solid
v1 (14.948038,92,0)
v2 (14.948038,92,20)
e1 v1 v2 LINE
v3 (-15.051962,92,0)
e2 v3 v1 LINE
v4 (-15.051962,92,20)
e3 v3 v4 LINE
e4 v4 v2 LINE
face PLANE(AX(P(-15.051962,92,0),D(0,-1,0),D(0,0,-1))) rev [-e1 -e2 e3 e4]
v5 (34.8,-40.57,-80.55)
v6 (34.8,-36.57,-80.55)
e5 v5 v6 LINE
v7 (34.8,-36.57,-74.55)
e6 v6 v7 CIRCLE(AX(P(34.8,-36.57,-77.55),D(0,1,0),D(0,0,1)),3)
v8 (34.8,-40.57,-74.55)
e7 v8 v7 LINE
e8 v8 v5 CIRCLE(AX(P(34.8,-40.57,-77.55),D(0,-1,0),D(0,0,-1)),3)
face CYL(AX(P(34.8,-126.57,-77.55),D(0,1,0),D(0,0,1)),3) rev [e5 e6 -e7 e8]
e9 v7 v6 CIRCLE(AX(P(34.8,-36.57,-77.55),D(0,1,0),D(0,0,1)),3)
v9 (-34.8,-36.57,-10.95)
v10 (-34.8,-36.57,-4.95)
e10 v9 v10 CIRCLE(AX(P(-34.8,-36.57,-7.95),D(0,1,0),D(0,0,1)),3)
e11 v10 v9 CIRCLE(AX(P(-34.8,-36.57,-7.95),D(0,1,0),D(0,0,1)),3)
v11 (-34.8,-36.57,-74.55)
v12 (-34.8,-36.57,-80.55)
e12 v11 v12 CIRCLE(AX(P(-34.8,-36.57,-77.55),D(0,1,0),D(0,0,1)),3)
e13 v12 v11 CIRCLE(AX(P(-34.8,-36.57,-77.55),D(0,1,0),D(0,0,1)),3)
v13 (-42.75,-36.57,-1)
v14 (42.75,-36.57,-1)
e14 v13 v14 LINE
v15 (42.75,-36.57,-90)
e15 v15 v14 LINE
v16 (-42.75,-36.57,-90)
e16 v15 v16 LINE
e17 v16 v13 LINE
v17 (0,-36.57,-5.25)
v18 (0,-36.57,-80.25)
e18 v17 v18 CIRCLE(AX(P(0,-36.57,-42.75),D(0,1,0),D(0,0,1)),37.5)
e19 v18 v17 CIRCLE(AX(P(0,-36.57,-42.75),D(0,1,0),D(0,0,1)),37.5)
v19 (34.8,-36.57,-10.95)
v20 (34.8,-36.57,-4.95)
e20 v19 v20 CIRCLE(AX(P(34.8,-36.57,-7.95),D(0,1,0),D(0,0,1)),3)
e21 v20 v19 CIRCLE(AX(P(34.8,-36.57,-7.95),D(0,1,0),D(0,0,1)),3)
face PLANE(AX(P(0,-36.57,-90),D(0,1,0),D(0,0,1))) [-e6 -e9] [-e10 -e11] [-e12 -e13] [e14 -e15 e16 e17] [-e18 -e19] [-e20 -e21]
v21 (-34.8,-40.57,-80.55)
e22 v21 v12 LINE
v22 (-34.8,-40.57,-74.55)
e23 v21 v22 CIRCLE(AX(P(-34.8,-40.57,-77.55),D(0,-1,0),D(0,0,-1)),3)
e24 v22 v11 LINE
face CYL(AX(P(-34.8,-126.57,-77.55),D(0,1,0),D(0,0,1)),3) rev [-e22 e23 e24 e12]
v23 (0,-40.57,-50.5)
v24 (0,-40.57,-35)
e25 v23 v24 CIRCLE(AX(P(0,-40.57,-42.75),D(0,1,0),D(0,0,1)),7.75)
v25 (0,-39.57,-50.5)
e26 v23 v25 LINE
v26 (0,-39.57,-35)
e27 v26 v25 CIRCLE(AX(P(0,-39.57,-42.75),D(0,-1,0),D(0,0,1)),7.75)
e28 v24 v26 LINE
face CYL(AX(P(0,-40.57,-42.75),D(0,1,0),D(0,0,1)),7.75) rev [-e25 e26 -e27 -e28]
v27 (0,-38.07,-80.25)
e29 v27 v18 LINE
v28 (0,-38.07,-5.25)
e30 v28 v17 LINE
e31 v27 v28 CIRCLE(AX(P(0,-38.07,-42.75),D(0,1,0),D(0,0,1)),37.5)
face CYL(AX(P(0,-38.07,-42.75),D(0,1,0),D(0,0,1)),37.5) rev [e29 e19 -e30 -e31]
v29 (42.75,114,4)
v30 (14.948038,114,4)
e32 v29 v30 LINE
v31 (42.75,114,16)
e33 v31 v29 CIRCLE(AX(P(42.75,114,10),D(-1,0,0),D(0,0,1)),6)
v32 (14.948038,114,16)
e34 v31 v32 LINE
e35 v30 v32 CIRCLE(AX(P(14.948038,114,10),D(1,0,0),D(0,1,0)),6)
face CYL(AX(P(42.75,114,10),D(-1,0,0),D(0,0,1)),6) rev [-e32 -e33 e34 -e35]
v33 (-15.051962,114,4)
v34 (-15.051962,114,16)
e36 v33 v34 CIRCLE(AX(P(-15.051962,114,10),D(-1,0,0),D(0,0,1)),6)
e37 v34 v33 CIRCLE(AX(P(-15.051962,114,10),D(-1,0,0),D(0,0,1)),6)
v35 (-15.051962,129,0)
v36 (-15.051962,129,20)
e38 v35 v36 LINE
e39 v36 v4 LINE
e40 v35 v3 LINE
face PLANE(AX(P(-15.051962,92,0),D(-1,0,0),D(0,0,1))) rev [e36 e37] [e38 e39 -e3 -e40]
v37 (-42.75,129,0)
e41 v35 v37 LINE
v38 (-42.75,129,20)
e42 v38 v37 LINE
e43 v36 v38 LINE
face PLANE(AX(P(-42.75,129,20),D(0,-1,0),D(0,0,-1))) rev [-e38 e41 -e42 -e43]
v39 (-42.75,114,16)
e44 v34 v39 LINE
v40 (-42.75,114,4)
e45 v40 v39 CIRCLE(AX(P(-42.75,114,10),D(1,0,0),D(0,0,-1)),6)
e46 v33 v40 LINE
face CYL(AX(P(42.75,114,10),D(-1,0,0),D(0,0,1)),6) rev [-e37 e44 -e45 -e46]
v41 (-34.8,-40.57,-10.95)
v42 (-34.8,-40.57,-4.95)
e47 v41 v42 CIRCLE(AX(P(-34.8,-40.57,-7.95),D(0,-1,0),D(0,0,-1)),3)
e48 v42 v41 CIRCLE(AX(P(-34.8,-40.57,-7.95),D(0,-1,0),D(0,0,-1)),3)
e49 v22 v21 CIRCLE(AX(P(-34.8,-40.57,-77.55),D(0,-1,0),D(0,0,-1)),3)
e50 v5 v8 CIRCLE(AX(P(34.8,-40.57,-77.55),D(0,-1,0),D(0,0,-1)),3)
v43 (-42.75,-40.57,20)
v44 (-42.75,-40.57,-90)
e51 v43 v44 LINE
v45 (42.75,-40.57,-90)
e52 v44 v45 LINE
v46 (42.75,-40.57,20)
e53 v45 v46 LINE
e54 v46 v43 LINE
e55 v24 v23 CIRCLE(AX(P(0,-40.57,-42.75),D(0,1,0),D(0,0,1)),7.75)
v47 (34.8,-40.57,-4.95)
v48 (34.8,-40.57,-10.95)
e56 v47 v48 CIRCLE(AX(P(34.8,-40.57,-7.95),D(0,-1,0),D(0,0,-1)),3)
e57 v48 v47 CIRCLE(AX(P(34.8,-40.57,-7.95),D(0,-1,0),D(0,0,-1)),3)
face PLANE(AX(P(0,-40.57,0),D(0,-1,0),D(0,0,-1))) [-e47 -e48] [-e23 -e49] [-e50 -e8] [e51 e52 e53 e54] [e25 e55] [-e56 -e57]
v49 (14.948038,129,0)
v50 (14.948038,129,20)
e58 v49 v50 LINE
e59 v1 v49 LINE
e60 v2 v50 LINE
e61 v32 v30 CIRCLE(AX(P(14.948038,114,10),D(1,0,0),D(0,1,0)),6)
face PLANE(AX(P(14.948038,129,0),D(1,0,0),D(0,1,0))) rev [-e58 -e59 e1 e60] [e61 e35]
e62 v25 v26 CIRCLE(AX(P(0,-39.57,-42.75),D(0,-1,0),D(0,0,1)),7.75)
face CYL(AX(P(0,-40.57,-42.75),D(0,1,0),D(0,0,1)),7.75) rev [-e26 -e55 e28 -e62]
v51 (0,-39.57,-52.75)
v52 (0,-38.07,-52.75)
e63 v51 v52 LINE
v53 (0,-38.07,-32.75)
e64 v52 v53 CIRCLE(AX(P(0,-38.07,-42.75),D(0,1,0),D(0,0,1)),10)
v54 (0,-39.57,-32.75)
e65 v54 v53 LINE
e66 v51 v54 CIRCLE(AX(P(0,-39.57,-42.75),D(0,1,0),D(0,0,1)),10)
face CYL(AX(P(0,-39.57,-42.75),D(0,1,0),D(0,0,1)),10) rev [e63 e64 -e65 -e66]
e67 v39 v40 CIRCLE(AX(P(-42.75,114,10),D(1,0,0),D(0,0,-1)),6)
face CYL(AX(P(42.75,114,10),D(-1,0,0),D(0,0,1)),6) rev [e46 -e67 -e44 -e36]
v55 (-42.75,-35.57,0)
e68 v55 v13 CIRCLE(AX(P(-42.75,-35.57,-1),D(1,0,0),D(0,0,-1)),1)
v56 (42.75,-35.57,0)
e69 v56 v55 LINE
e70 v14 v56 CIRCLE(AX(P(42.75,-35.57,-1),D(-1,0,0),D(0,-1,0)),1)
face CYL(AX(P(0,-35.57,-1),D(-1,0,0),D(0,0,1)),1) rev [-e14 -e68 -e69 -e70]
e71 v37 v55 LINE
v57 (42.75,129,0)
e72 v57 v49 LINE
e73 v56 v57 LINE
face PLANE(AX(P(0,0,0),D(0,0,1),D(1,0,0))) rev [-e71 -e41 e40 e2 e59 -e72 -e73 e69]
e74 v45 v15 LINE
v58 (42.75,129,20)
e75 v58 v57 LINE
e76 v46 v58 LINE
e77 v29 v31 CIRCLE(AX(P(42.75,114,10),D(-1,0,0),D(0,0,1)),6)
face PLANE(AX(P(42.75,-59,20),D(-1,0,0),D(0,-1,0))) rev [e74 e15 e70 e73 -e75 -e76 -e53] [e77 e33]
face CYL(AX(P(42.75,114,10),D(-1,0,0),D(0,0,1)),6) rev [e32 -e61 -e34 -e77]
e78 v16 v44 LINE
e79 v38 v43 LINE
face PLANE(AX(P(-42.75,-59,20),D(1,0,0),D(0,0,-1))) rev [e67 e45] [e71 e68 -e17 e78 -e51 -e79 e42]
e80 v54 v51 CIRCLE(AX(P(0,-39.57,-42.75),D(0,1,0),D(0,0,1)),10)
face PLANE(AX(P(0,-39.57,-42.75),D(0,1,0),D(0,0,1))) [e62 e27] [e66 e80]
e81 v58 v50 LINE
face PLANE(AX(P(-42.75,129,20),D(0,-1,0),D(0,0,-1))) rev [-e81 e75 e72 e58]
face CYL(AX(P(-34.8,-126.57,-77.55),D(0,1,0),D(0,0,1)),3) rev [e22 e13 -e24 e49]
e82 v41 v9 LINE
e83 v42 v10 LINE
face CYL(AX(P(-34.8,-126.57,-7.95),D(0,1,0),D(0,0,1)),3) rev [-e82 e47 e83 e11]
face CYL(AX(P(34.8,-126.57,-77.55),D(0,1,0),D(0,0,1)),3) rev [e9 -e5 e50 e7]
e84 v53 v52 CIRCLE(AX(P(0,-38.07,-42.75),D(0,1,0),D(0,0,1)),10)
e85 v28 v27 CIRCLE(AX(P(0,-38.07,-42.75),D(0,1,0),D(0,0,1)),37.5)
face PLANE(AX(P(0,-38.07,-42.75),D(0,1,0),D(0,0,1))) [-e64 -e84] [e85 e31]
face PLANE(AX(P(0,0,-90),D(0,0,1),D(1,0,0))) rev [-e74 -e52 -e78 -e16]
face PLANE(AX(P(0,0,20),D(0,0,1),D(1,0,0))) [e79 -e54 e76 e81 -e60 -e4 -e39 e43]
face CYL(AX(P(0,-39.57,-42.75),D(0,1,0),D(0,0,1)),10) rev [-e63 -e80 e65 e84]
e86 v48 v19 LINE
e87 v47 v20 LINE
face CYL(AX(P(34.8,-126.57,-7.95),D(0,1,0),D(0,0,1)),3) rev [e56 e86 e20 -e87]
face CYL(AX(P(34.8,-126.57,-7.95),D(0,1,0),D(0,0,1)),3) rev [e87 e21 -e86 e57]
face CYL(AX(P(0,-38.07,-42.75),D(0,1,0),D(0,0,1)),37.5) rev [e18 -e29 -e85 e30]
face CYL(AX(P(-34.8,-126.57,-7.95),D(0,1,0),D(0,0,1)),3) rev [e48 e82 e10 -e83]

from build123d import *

# Parameters (mm, degrees)
EXTRUDE_1_DEPTH          = 20
SKETCH_2_W               = 30
SKETCH_2_H               = 37
CUT_EXTRUDE_1_DEPTH      = 20
CUT_EXTRUDE_2_DEPTH      = 157.04887055
CUT_EXTRUDE_2_DEPTH_BACK = 157.04887055
SKETCH_3_R               = 6
CUT_EXTRUDE_3_DEPTH      = 138.362886181
CUT_EXTRUDE_3_DEPTH_BACK = 138.362886181
SKETCH_4_W               = 85.5
SKETCH_4_H               = 10
SKETCH_5_W               = 85.5
SKETCH_5_H               = 20
CUT_EXTRUDE_4_DEPTH      = 8.43
EXTRUDE_START            = -20
SKETCH_6_W               = 85.5
SKETCH_6_H               = 4
EXTRUDE_2_DEPTH          = 90
SKETCH_8_R               = 3
CUT_EXTRUDE_6_DEPTH      = 90
FILLET_1_R               = 1
SKETCH_9_R               = 37.5
CUT_EXTRUDE_7_DEPTH      = 1.5
CUT_EXTRUDE_8_DEPTH      = 195.524927451
CUT_EXTRUDE_8_DEPTH_BACK = 195.524927451
SKETCH_10_R              = 7.75
SKETCH_11_R              = 10
CUT_EXTRUDE_9_DEPTH      = 1.5


with BuildPart() as part:
    # 草图1 → 凸台-拉伸1 (new body)
    with BuildSketch(Plane.XY):
        Polygon((-42.75, -59), (-42.75, 59), (-42.75, 129), (42.75, 129), (42.75, 59), (42.75, -59), align=None)
    extrude(amount=EXTRUDE_1_DEPTH)

    # 草图2 → 切除-拉伸1 (cut)
    with BuildSketch(Plane.XY.offset(20)):
        with Locations((-0.051962385, 110.5)):
            Rectangle(SKETCH_2_W, SKETCH_2_H)
    extrude(amount=-CUT_EXTRUDE_1_DEPTH, mode=Mode.SUBTRACT)

    # 草图3 → 切除-拉伸2 (cut, two sides: drawn at the far end of the back side and taken through both)
    with BuildSketch(Plane.ZY.offset(42.75).offset(-CUT_EXTRUDE_2_DEPTH_BACK)):
        with Locations((10, 114)):
            Circle(SKETCH_3_R)
    extrude(amount=CUT_EXTRUDE_2_DEPTH + CUT_EXTRUDE_2_DEPTH_BACK, mode=Mode.SUBTRACT)

    # 草图4 → 切除-拉伸3 (cut, two sides: drawn at the far end of the back side and taken through both)
    with BuildSketch(Plane.XY.offset(20).offset(-CUT_EXTRUDE_3_DEPTH_BACK)):
        with Locations((0, -54)):
            Rectangle(SKETCH_4_W, SKETCH_4_H)
    extrude(amount=CUT_EXTRUDE_3_DEPTH + CUT_EXTRUDE_3_DEPTH_BACK, mode=Mode.SUBTRACT)

    # 草图5 → 切除-拉伸4 (cut)
    with BuildSketch(Plane.XZ.offset(49)):
        with Locations((0, 10)):
            Rectangle(SKETCH_5_W, SKETCH_5_H)
    extrude(amount=-CUT_EXTRUDE_4_DEPTH, mode=Mode.SUBTRACT)

    # 草图6 → 凸台-拉伸2 (add)
    with BuildSketch(Plane.XY.offset(20).offset(EXTRUDE_START)):
        with Locations((0, -38.57)):
            Rectangle(SKETCH_6_W, SKETCH_6_H)
    extrude(amount=-EXTRUDE_2_DEPTH)

    # 草图8 → 切除-拉伸6 (cut)
    with BuildSketch(Plane(origin=(0, -36.57, 0), x_dir=(1, 0, 0), z_dir=(0, 1, 0))):
        with Locations(Location((-34.8, 77.55, 0), (0, 0, 270))):
            Circle(SKETCH_8_R)
        with Locations(Location((34.8, 77.55, 0), (0, 0, 270))):
            Circle(SKETCH_8_R)
        with Locations(Location((-34.8, 7.95, 0), (0, 0, 270))):
            Circle(SKETCH_8_R)
        with Locations(Location((34.8, 7.95, 0), (0, 0, 270))):
            Circle(SKETCH_8_R)
    extrude(amount=-CUT_EXTRUDE_6_DEPTH, mode=Mode.SUBTRACT)

    # 圆角1
    fillet_1_edges = [part.edges().sort_by_distance(p)[0] for p in [
        (0, -36.57, 0),
    ]]
    fillet(fillet_1_edges, radius=FILLET_1_R)

    # 草图9 → 切除-拉伸7 (cut)
    with BuildSketch(Plane(origin=(0, -36.57, 0), x_dir=(1, 0, 0), z_dir=(0, 1, 0))):
        with Locations(Location((0, 42.75, 0), (0, 0, 270))):
            Circle(SKETCH_9_R)
    extrude(amount=-CUT_EXTRUDE_7_DEPTH, mode=Mode.SUBTRACT)

    # 草图10 → 切除-拉伸8 (cut, two sides: drawn at the far end of the back side and taken through both)
    with BuildSketch(Plane(origin=(0, -38.07, 0), x_dir=(1, 0, 0), z_dir=(0, 1, 0)).offset(-CUT_EXTRUDE_8_DEPTH_BACK)):
        with Locations(Location((0, 42.75, 0), (0, 0, 270))):
            Circle(SKETCH_10_R)
    extrude(amount=CUT_EXTRUDE_8_DEPTH + CUT_EXTRUDE_8_DEPTH_BACK, mode=Mode.SUBTRACT)

    # 草图11 → 切除-拉伸9 (cut)
    with BuildSketch(Plane(origin=(0, -38.07, 0), x_dir=(1, 0, 0), z_dir=(0, 1, 0))):
        with Locations(Location((0, 42.75, 0), (0, 0, 270))):
            Circle(SKETCH_11_R)
    extrude(amount=-CUT_EXTRUDE_9_DEPTH, mode=Mode.SUBTRACT)


solid = part.part
